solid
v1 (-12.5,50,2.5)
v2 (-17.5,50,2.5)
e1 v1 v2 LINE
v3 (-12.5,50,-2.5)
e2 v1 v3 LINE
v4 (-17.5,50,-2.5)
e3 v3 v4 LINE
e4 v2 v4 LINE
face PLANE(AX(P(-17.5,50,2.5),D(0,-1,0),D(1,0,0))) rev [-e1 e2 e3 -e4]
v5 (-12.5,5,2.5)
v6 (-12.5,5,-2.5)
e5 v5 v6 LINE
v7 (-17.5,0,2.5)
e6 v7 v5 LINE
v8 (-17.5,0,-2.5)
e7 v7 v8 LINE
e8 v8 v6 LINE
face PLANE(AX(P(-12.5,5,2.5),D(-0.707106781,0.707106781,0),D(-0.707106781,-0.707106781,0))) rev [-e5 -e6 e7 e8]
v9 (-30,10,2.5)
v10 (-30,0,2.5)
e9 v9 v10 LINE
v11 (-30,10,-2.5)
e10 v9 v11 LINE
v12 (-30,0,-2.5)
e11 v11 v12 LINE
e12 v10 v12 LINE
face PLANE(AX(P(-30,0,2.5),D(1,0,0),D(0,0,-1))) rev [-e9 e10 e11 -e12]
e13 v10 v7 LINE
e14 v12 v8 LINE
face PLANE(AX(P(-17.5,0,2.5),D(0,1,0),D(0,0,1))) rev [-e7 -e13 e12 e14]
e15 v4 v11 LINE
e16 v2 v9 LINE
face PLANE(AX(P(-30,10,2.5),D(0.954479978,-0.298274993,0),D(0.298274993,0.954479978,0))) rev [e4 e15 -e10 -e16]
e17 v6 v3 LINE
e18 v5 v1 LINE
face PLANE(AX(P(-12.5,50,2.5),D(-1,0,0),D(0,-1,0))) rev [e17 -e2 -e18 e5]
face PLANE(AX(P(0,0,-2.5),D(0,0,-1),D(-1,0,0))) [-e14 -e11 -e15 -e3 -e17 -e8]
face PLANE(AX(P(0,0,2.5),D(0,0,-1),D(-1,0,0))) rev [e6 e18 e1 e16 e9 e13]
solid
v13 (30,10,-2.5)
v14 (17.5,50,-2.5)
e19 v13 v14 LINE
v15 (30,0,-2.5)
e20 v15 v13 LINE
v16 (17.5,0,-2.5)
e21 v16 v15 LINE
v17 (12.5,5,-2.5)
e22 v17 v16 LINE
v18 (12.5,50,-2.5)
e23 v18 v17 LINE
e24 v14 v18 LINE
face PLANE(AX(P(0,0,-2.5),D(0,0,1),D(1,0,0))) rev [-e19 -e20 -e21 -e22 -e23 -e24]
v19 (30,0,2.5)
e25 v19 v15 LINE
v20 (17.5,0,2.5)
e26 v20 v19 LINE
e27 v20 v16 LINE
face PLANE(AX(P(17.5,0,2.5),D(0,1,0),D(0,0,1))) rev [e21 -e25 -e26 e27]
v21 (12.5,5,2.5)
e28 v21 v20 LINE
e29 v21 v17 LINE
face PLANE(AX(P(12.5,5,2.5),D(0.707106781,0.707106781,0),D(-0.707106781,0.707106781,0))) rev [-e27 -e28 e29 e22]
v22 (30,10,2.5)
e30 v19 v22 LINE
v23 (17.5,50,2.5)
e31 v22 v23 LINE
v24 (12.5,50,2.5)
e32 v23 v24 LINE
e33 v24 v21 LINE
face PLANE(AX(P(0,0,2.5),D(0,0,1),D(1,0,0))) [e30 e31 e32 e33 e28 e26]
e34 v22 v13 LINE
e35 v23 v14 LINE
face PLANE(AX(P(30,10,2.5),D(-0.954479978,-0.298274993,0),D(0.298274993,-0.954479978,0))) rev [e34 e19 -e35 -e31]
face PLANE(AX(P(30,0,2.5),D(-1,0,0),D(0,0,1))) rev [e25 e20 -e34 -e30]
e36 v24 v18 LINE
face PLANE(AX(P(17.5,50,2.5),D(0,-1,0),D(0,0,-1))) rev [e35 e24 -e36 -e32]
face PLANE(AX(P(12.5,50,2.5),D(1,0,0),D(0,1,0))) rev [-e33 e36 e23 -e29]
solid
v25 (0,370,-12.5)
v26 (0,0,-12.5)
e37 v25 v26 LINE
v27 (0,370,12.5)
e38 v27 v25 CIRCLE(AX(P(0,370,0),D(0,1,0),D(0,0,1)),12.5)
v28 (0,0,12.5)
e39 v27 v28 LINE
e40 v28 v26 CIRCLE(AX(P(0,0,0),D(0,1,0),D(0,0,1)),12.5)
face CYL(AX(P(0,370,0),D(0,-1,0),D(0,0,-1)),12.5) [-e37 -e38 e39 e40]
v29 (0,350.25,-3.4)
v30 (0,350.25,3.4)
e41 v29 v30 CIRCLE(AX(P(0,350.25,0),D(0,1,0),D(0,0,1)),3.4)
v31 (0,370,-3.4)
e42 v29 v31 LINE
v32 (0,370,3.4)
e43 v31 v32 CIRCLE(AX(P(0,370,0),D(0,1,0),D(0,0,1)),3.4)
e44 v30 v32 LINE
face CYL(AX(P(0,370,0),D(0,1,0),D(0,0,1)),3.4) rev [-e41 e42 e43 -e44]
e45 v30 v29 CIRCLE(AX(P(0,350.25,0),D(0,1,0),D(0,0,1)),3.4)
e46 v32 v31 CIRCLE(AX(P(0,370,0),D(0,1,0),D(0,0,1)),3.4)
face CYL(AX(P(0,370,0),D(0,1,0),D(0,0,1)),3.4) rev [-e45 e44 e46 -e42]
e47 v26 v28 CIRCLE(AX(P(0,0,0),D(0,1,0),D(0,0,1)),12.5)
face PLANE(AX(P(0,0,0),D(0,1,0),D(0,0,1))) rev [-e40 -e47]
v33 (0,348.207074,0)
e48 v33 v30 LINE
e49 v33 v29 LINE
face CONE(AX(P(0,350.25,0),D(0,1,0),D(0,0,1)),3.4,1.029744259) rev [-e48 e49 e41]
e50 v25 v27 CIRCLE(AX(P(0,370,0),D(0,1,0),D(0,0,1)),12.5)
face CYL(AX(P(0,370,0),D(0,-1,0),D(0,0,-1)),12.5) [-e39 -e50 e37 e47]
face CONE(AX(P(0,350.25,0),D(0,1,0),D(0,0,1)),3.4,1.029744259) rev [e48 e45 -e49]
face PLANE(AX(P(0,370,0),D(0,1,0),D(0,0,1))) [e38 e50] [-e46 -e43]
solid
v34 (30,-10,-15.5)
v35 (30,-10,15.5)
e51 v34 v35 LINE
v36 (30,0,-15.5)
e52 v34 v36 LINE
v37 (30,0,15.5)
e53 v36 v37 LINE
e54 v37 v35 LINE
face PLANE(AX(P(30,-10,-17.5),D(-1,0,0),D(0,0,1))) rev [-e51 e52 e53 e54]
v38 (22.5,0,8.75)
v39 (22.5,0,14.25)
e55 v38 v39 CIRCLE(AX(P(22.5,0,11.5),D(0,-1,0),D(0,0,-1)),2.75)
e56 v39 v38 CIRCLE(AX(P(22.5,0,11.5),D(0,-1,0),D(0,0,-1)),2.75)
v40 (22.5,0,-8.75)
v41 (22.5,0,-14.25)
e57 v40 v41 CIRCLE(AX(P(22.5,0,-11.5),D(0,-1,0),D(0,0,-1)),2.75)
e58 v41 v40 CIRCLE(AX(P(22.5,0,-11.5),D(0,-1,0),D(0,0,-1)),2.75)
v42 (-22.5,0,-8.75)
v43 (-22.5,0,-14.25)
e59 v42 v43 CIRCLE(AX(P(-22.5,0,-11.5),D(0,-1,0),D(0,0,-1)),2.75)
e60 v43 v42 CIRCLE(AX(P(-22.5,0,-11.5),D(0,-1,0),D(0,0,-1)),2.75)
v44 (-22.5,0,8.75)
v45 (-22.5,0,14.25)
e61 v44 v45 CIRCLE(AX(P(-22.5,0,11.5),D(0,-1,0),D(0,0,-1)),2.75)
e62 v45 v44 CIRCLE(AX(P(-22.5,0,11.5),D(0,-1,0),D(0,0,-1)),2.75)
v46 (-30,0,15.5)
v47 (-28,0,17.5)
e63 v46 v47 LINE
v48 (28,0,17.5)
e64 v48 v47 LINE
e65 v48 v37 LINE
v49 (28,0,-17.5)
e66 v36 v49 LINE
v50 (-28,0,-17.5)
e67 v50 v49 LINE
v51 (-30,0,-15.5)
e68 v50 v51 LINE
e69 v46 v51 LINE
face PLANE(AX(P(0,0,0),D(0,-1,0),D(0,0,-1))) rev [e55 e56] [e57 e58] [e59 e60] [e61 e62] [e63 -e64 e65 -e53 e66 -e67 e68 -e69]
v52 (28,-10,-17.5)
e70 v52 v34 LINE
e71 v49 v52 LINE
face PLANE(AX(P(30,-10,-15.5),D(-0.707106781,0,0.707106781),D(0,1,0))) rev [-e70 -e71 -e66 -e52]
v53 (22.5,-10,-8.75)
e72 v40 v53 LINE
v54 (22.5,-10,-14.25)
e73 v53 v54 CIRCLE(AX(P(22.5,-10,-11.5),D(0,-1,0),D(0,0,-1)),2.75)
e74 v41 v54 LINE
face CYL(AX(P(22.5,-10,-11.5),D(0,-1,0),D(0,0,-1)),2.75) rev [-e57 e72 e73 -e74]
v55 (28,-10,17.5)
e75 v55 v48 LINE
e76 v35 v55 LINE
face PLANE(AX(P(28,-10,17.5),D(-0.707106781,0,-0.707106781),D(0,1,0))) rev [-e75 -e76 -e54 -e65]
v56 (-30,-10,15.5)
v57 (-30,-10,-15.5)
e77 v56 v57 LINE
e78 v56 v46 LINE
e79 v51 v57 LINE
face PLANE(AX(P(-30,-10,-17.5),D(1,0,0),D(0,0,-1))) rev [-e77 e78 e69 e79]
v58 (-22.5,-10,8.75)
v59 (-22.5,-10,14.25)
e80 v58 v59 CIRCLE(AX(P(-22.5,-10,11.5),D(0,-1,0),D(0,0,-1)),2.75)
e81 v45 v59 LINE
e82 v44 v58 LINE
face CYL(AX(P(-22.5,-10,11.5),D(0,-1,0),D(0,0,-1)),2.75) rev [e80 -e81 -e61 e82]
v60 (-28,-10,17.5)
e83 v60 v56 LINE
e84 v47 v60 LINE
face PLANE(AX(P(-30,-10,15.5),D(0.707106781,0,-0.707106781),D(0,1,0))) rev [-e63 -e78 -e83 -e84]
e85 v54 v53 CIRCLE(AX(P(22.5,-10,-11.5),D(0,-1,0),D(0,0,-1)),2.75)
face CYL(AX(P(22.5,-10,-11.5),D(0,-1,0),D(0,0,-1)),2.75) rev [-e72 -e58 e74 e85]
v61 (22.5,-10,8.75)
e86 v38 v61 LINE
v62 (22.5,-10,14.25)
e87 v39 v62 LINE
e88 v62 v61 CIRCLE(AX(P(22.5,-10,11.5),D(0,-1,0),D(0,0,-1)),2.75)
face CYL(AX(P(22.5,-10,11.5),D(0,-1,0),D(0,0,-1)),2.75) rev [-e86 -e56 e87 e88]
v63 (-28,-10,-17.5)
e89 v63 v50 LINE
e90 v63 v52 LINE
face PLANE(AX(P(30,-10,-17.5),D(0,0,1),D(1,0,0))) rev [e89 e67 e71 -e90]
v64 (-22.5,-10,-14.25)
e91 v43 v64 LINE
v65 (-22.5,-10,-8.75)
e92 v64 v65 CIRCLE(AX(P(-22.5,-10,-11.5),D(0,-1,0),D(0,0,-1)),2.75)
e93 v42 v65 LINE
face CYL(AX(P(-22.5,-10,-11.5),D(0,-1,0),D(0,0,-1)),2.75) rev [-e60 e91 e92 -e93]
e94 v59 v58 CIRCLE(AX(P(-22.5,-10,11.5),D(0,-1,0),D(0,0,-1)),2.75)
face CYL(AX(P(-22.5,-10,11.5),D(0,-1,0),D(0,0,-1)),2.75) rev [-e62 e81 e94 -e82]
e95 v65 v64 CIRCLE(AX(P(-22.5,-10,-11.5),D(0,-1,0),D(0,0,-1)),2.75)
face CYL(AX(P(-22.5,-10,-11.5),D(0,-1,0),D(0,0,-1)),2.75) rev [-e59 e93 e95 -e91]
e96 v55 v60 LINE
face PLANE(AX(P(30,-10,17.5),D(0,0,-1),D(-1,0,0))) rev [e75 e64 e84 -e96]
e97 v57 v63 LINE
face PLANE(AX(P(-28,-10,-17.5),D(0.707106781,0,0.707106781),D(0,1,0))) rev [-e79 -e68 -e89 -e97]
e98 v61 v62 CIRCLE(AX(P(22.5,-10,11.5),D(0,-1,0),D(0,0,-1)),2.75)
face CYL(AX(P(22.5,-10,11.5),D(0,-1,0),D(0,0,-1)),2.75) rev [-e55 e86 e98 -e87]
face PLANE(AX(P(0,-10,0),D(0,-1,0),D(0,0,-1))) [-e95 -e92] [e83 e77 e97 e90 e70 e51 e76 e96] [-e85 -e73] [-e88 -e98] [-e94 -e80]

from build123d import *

# Parameters (mm, degrees)
SKETCH_1_R                  = 12.5
EXTRUDE_1_DEPTH             = 370
SKETCH_2_W                  = 60
SKETCH_2_H                  = 35
EXTRUDE_2_DEPTH             = 10
EXTRUDE_3_DEPTH             = 2.5
EXTRUDE_3_2_DEPTH           = 2.5
SKETCH_5_W                  = 2.75
SKETCH_5_H                  = 10.001
HOLE_WIZARD_M5_1_AT_2_COUNT = 2
HOLE_WIZARD_M5_1_AT_2_PITCH = 45
HOLE_WIZARD_M5_1_AT_3_COUNT = 2
HOLE_WIZARD_M5_1_AT_3_PITCH = 50.537115074
HOLE_WIZARD_M5_1_AT_4_COUNT = 2
HOLE_WIZARD_M5_1_AT_4_PITCH = 23
CHAMFER_1_SIZE              = 2


with BuildPart() as part:
    # 草图1 → 凸台-拉伸1 (new body)
    with BuildSketch(Plane(origin=(0, 0, 0), x_dir=(1, 0, 0), z_dir=(0, 1, 0))):
        with Locations(Location((0, 0, 0), (0, 0, 270))):
            Circle(SKETCH_1_R)
    extrude(amount=EXTRUDE_1_DEPTH)

    # 草图7 → M8 螺纹孔1 (revolve, cut)
    with BuildSketch(Plane(origin=(0, 370, 0), x_dir=(0, 0, 1), z_dir=(1, 0, 0))):
        Polygon((0, 0), (0, 21.792926105), (3.4, 19.75), (3.4, 0), align=None)
    revolve(axis=Axis((0, 376.35, 0), (0, -1, 0)), mode=Mode.SUBTRACT)


with BuildPart() as body_2:
    # 草图2 → 凸台-拉伸2 (new body)
    with BuildSketch(Plane.XZ):
        Rectangle(SKETCH_2_W, SKETCH_2_H)
    extrude(amount=EXTRUDE_2_DEPTH)

    # 草图5 → M5 间隙孔1 (revolve, cut)
    with BuildSketch(Plane(origin=(-22.5, -10, 11.5), x_dir=(0, 0, -1), z_dir=(1, 0, 0))):
        with Locations((1.375, 5.0005)):
            Rectangle(SKETCH_5_W, SKETCH_5_H)
    hole_wizard_m5_1 = revolve(axis=Axis((-22.5, -16.35, 11.5), (0, 1, 0)), mode=Mode.SUBTRACT)

    # M5 间隙孔1 at 2: M5 间隙孔1 ×2
    with Locations(*[(i * HOLE_WIZARD_M5_1_AT_2_PITCH, 0, 0) for i in range(1, HOLE_WIZARD_M5_1_AT_2_COUNT)]):
        add(hole_wizard_m5_1, mode=Mode.SUBTRACT)

    # M5 间隙孔1 at 3: M5 间隙孔1 ×2
    with Locations(*[Vector(0.8904346821960805, 0, -0.45511105978910815) * (i * HOLE_WIZARD_M5_1_AT_3_PITCH) for i in range(1, HOLE_WIZARD_M5_1_AT_3_COUNT)]):
        add(hole_wizard_m5_1, mode=Mode.SUBTRACT)

    # M5 间隙孔1 at 4: M5 间隙孔1 ×2
    with Locations(*[(0, 0, -i * HOLE_WIZARD_M5_1_AT_4_PITCH) for i in range(1, HOLE_WIZARD_M5_1_AT_4_COUNT)]):
        add(hole_wizard_m5_1, mode=Mode.SUBTRACT)

    # 倒角1
    chamfer_1_edges = [body_2.edges().sort_by_distance(p)[0] for p in [
        (-30, -5, 17.5),
        (30, -5, 17.5),
        (30, -5, -17.5),
        (-30, -5, -17.5),
    ]]
    chamfer(chamfer_1_edges, length=CHAMFER_1_SIZE)


with BuildPart() as body_3:
    # 草图3 → 凸台-拉伸3 (new, symmetric)
    with BuildSketch(Plane.XY):
        Polygon((30, 0), (30, 10), (17.5, 50), (12.5, 50), (12.5, 5), (17.5, 0), align=None)
    extrude(amount=EXTRUDE_3_DEPTH, both=True)


with BuildPart() as body_4:
    # 草图3 → Extrude 3 2 (new, symmetric)
    with BuildSketch(Plane.XY):
        Polygon((-12.5, 5), (-17.5, 0), (-30, 0), (-30, 10), (-17.5, 50), (-12.5, 50), align=None)
    extrude(amount=EXTRUDE_3_2_DEPTH, both=True)


solid = Compound([part.part, body_2.part, body_3.part, body_4.part])
